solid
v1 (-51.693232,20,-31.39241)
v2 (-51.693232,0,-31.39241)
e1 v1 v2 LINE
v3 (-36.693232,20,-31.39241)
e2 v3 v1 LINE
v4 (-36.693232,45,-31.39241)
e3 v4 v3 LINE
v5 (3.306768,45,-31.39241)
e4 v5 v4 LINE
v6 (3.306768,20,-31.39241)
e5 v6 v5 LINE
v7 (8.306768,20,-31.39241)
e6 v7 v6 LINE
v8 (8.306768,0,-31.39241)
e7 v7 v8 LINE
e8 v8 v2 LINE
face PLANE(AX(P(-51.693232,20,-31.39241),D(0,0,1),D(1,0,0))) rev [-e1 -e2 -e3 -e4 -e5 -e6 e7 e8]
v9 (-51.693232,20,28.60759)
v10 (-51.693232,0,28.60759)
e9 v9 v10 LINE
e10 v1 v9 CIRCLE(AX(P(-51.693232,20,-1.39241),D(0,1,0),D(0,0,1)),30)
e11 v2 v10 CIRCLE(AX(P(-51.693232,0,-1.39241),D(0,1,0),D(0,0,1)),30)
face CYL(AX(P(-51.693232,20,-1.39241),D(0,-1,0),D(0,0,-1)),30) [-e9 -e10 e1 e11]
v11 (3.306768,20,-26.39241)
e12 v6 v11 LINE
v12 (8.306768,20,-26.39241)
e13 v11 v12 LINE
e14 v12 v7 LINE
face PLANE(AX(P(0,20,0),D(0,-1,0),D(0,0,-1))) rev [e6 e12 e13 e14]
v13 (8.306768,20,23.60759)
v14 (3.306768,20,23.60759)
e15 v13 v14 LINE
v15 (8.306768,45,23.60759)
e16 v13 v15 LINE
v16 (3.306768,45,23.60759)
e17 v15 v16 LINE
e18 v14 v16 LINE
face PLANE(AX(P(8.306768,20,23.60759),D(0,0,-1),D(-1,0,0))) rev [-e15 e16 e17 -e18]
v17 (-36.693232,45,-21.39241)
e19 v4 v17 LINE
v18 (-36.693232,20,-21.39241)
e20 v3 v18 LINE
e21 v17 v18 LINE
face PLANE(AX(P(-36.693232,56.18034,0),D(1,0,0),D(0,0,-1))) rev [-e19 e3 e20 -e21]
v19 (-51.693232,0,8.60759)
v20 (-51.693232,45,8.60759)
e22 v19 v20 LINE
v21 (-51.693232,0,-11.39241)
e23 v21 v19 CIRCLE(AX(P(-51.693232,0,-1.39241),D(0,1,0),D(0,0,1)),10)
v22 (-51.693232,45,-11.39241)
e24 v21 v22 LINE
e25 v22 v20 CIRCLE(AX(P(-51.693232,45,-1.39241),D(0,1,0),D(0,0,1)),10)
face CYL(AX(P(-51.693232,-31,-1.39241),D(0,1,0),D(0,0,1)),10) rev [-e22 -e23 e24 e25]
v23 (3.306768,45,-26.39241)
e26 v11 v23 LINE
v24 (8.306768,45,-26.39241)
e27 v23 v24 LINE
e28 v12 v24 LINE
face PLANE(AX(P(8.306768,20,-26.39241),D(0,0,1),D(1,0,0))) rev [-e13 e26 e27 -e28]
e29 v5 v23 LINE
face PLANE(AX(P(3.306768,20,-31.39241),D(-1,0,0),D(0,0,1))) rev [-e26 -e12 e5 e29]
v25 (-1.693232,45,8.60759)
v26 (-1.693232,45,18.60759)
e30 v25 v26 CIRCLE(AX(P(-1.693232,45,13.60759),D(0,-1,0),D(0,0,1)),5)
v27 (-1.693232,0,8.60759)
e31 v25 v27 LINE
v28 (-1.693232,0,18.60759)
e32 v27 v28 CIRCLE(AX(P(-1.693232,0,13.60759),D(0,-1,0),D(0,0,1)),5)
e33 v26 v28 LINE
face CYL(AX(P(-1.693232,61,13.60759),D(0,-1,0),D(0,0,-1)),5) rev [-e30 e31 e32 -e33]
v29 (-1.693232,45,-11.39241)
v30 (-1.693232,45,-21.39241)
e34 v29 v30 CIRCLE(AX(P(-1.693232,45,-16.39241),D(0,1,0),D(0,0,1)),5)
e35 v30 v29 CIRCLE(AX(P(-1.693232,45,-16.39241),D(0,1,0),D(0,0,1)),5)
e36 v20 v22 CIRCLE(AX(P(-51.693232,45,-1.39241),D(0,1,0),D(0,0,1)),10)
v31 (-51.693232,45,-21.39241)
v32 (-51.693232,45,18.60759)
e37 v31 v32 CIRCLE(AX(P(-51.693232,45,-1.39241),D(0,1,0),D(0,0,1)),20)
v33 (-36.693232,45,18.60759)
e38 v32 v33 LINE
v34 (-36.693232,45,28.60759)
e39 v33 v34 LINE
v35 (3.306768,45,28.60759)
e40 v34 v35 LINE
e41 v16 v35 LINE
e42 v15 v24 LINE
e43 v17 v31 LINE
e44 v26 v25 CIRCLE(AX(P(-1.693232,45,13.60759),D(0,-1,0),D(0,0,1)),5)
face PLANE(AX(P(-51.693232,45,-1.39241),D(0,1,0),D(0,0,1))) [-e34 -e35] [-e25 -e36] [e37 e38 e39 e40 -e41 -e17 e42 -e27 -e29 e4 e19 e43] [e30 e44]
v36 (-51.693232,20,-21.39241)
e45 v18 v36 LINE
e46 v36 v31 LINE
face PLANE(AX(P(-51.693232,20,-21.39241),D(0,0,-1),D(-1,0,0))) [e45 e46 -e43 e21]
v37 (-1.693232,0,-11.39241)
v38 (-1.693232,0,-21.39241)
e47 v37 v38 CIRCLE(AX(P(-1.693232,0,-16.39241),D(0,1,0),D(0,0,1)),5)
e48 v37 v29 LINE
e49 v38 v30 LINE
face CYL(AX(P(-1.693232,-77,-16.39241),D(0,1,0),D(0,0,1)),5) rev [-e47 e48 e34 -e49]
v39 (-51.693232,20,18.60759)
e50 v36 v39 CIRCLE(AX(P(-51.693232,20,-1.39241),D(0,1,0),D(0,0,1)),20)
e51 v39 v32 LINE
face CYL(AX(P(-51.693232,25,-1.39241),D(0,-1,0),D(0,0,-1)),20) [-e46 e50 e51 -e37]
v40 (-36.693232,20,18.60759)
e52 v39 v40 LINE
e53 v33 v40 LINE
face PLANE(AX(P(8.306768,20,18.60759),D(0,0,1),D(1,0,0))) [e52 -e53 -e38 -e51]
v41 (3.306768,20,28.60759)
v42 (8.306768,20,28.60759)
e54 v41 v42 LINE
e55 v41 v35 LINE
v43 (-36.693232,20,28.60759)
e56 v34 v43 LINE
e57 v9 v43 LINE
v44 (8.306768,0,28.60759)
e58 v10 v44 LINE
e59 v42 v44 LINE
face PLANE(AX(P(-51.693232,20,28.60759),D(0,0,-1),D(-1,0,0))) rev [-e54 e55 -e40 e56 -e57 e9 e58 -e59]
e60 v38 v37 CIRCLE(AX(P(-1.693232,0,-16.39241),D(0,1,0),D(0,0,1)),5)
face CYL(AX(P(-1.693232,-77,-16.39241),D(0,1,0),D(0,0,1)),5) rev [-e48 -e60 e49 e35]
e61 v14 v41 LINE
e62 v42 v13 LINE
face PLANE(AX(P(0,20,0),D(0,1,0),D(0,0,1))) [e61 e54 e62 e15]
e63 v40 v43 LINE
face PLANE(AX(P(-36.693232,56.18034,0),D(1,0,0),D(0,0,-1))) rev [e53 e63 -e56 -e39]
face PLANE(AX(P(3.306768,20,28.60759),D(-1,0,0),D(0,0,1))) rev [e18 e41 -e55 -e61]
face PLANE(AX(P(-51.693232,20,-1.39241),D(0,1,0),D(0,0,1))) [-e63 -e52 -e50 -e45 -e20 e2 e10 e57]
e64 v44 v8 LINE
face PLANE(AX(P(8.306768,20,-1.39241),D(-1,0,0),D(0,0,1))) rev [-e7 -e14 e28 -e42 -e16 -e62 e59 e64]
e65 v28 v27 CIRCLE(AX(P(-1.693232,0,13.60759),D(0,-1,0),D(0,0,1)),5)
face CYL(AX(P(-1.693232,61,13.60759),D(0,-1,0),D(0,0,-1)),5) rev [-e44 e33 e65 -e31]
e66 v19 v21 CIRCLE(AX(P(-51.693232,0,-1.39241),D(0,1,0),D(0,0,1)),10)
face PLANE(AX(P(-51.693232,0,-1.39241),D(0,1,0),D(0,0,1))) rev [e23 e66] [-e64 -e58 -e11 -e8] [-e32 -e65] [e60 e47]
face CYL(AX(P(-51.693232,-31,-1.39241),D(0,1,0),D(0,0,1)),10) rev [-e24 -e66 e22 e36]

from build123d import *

# Parameters (mm, degrees)
BASE_BLOCK_DEPTH        = 20
STEP_PAD_1_DEPTH        = 5
STEP_START              = -5
STEP_PAD_2_DEPTH        = 5
ROUND_BOSS_SKETCH_R     = 20
ROUND_BOSS_DEPTH        = 20
RISER_BLOCK_1_DEPTH     = 20
SIDE_PAD_1_SKETCH_W     = 40
SIDE_PAD_1_SKETCH_H     = 10
SIDE_PAD_1_DEPTH        = 5
RISER_BLOCK_2_SKETCH_W  = 40
RISER_BLOCK_2_SKETCH_H  = 10
RISER_BLOCK_2_DEPTH     = 20
SIDE_PAD_2_SKETCH_W     = 40
SIDE_PAD_2_SKETCH_H     = 10
SIDE_PAD_2_DEPTH        = 5
RISER_BLOCK_3_SKETCH_W  = 40
RISER_BLOCK_3_SKETCH_H  = 10
RISER_BLOCK_3_DEPTH     = 20
BORE_20_SKETCH_R        = 10
BORE_20_DEPTH           = 76
CORNER_SLOT_1_SKETCH_W  = 5
CORNER_SLOT_1_SKETCH_H  = 5
CORNER_SLOT_1_5X5_DEPTH = 25
CORNER_SLOT_2_SKETCH_W  = 5
CORNER_SLOT_2_SKETCH_H  = 5
CORNER_SLOT_2_5X5_DEPTH = 25
HOLE_1_DEPTH            = 16
HOLE_1_DEPTH_BACK       = 53
HOLE_1_SKETCH_R         = 5
HOLE_2_SKETCH_R         = 5
HOLE_2_DEPTH            = 122
TOP_BLOCK_SKETCH_W      = 5
TOP_BLOCK_SKETCH_H      = 10
TOP_BLOCK_45_DEPTH      = 25


with BuildPart() as part:
    # Base Profile Sketch → Base Block (new body)
    with BuildSketch(Plane(origin=(0, 0, 0), x_dir=(1, 0, 0), z_dir=(0, 1, 0))):
        with BuildLine():
            Line((8.306767896, 1.392410292), (8.306767896, 31.392410292))
            Line((8.306767896, 31.392410292), (-51.693232104, 31.392410292))
            ThreePointArc((-51.693232104, 31.392410292), (-81.693232104, 1.392410292), (-51.693232104, -28.607589708))
            Line((-51.693232104, -28.607589708), (8.306767896, -28.607589708))
            Line((8.306767896, -28.607589708), (8.306767896, 1.392410292))
        make_face()
    extrude(amount=BASE_BLOCK_DEPTH)

    # Step Pad 1 Sketch → Step Pad 1 (add)
    with BuildSketch(Plane(origin=(0, 20, 0), x_dir=(1, 0, 0), z_dir=(0, 1, 0))):
        with BuildLine():
            ThreePointArc((-31.693232104, 1.392410292), (-37.55109648, 15.534545916), (-51.693232104, 21.392410292))
            ThreePointArc((-51.693232104, 21.392410292), (-71.693232104, 1.392410292), (-51.693232104, -18.607589708))
            ThreePointArc((-51.693232104, -18.607589708), (-37.55109648, -12.749725331), (-31.693232104, 1.392410292))
        make_face()
    extrude(amount=STEP_PAD_1_DEPTH)

    # Step Pad 2 Sketch → Step Pad 2 (add)
    with BuildSketch(Plane(origin=(0, 25, 0), x_dir=(1, 0, 0), z_dir=(0, 1, 0)).offset(STEP_START)):
        with BuildLine():
            Line((-51.693232104, 21.392410292), (8.306767896, 21.392410292))
            Line((8.306767896, 21.392410292), (8.306767896, -18.607589708))
            Line((8.306767896, -18.607589708), (-51.693232104, -18.607589708))
            ThreePointArc((-51.693232104, -18.607589708), (-71.693232104, 1.392410292), (-51.693232104, 21.392410292))
        make_face()
    extrude(amount=STEP_PAD_2_DEPTH)

    # Round Boss Sketch → Round Boss (add)
    with BuildSketch(Plane(origin=(0, 25, 0), x_dir=(1, 0, 0), z_dir=(0, 1, 0))):
        with Locations(Location((-51.693232104, 1.392410292, 0), (0, 0, 270))):
            Circle(ROUND_BOSS_SKETCH_R)
    extrude(amount=ROUND_BOSS_DEPTH)

    # Riser Block 1 Sketch → Riser Block 1 (add)
    with BuildSketch(Plane(origin=(0, 25, 0), x_dir=(1, 0, 0), z_dir=(0, 1, 0))):
        with BuildLine():
            Line((8.306767896, 21.392410292), (-51.693232104, 21.392410292))
            ThreePointArc((-51.693232104, 21.392410292), (-31.693232104, 1.392410292), (-51.693232104, -18.607589708))
            Line((-51.693232104, -18.607589708), (8.306767896, -18.607589708))
            Line((8.306767896, -18.607589708), (8.306767896, 21.392410292))
        make_face()
    extrude(amount=RISER_BLOCK_1_DEPTH)

    # Side Pad 1 Sketch → Side Pad 1 (add)
    with BuildSketch(Plane(origin=(0, 20, 0), x_dir=(1, 0, 0), z_dir=(0, 1, 0))):
        with Locations((-11.693232104, 26.392410292)):
            Rectangle(SIDE_PAD_1_SKETCH_W, SIDE_PAD_1_SKETCH_H)
    extrude(amount=SIDE_PAD_1_DEPTH)

    # Riser Block 2 Sketch → Riser Block 2 (add)
    with BuildSketch(Plane(origin=(0, 25, 0), x_dir=(1, 0, 0), z_dir=(0, 1, 0))):
        with Locations((-11.693232104, 26.392410292)):
            Rectangle(RISER_BLOCK_2_SKETCH_W, RISER_BLOCK_2_SKETCH_H)
    extrude(amount=RISER_BLOCK_2_DEPTH)

    # Side Pad 2 Sketch → Side Pad 2 (add)
    with BuildSketch(Plane(origin=(0, 20, 0), x_dir=(1, 0, 0), z_dir=(0, 1, 0))):
        with Locations((-11.693232104, -23.607589708)):
            Rectangle(SIDE_PAD_2_SKETCH_W, SIDE_PAD_2_SKETCH_H)
    extrude(amount=SIDE_PAD_2_DEPTH)

    # Riser Block 3 Sketch → Riser Block 3 (add)
    with BuildSketch(Plane(origin=(0, 25, 0), x_dir=(1, 0, 0), z_dir=(0, 1, 0))):
        with Locations((-11.693232104, -23.607589708)):
            Rectangle(RISER_BLOCK_3_SKETCH_W, RISER_BLOCK_3_SKETCH_H)
    extrude(amount=RISER_BLOCK_3_DEPTH)

    # Bore Ø20 Sketch → Bore Ø20 (cut)
    with BuildSketch(Plane(origin=(0, 45, 0), x_dir=(1, 0, 0), z_dir=(0, 1, 0))):
        with Locations(Location((-51.693232104, 1.392410292, 0), (0, 0, 270))):
            Circle(BORE_20_SKETCH_R)
    extrude(amount=-BORE_20_DEPTH, mode=Mode.SUBTRACT)

    # Corner Slot 1 Sketch → Corner Slot 1 5x5 (cut)
    with BuildSketch(Plane(origin=(0, 45, 0), x_dir=(1, 0, 0), z_dir=(0, 1, 0))):
        with Locations((5.806767896, 28.892410292)):
            Rectangle(CORNER_SLOT_1_SKETCH_W, CORNER_SLOT_1_SKETCH_H)
    extrude(amount=-CORNER_SLOT_1_5X5_DEPTH, mode=Mode.SUBTRACT)

    # Corner Slot 2 Sketch → Corner Slot 2 5x5 (cut)
    with BuildSketch(Plane(origin=(0, 45, 0), x_dir=(1, 0, 0), z_dir=(0, 1, 0))):
        with Locations((5.806767896, -26.107589708)):
            Rectangle(CORNER_SLOT_2_SKETCH_W, CORNER_SLOT_2_SKETCH_H)
    extrude(amount=-CORNER_SLOT_2_5X5_DEPTH, mode=Mode.SUBTRACT)

    # Hole 1 Sketch → Hole 1 (cut, two sides: drawn at the far end of the back side and taken through both)
    with BuildSketch(Plane(origin=(0, 45, 0), x_dir=(1, 0, 0), z_dir=(0, 1, 0)).offset(-HOLE_1_DEPTH_BACK)):
        with Locations(Location((-1.693232104, -13.607589708, 0), (0, 0, 270))):
            Circle(HOLE_1_SKETCH_R)
    extrude(amount=HOLE_1_DEPTH + HOLE_1_DEPTH_BACK, mode=Mode.SUBTRACT)

    # Hole 2 Sketch → Hole 2 (cut)
    with BuildSketch(Plane(origin=(0, 45, 0), x_dir=(1, 0, 0), z_dir=(0, 1, 0))):
        with Locations(Location((-1.693232104, 16.392410292, 0), (0, 0, 270))):
            Circle(HOLE_2_SKETCH_R)
    extrude(amount=-HOLE_2_DEPTH, mode=Mode.SUBTRACT)

    # Top Block Sketch → Top Block 45 (add)
    with BuildSketch(Plane(origin=(0, 20, 0), x_dir=(1, 0, 0), z_dir=(0, 1, 0))):
        with Locations((-34.193232104, 26.392410292)):
            Rectangle(TOP_BLOCK_SKETCH_W, TOP_BLOCK_SKETCH_H)
        with Locations((-34.193232104, -23.607589708)):
            Rectangle(TOP_BLOCK_SKETCH_W, TOP_BLOCK_SKETCH_H)
    extrude(amount=TOP_BLOCK_45_DEPTH)


solid = part.part
